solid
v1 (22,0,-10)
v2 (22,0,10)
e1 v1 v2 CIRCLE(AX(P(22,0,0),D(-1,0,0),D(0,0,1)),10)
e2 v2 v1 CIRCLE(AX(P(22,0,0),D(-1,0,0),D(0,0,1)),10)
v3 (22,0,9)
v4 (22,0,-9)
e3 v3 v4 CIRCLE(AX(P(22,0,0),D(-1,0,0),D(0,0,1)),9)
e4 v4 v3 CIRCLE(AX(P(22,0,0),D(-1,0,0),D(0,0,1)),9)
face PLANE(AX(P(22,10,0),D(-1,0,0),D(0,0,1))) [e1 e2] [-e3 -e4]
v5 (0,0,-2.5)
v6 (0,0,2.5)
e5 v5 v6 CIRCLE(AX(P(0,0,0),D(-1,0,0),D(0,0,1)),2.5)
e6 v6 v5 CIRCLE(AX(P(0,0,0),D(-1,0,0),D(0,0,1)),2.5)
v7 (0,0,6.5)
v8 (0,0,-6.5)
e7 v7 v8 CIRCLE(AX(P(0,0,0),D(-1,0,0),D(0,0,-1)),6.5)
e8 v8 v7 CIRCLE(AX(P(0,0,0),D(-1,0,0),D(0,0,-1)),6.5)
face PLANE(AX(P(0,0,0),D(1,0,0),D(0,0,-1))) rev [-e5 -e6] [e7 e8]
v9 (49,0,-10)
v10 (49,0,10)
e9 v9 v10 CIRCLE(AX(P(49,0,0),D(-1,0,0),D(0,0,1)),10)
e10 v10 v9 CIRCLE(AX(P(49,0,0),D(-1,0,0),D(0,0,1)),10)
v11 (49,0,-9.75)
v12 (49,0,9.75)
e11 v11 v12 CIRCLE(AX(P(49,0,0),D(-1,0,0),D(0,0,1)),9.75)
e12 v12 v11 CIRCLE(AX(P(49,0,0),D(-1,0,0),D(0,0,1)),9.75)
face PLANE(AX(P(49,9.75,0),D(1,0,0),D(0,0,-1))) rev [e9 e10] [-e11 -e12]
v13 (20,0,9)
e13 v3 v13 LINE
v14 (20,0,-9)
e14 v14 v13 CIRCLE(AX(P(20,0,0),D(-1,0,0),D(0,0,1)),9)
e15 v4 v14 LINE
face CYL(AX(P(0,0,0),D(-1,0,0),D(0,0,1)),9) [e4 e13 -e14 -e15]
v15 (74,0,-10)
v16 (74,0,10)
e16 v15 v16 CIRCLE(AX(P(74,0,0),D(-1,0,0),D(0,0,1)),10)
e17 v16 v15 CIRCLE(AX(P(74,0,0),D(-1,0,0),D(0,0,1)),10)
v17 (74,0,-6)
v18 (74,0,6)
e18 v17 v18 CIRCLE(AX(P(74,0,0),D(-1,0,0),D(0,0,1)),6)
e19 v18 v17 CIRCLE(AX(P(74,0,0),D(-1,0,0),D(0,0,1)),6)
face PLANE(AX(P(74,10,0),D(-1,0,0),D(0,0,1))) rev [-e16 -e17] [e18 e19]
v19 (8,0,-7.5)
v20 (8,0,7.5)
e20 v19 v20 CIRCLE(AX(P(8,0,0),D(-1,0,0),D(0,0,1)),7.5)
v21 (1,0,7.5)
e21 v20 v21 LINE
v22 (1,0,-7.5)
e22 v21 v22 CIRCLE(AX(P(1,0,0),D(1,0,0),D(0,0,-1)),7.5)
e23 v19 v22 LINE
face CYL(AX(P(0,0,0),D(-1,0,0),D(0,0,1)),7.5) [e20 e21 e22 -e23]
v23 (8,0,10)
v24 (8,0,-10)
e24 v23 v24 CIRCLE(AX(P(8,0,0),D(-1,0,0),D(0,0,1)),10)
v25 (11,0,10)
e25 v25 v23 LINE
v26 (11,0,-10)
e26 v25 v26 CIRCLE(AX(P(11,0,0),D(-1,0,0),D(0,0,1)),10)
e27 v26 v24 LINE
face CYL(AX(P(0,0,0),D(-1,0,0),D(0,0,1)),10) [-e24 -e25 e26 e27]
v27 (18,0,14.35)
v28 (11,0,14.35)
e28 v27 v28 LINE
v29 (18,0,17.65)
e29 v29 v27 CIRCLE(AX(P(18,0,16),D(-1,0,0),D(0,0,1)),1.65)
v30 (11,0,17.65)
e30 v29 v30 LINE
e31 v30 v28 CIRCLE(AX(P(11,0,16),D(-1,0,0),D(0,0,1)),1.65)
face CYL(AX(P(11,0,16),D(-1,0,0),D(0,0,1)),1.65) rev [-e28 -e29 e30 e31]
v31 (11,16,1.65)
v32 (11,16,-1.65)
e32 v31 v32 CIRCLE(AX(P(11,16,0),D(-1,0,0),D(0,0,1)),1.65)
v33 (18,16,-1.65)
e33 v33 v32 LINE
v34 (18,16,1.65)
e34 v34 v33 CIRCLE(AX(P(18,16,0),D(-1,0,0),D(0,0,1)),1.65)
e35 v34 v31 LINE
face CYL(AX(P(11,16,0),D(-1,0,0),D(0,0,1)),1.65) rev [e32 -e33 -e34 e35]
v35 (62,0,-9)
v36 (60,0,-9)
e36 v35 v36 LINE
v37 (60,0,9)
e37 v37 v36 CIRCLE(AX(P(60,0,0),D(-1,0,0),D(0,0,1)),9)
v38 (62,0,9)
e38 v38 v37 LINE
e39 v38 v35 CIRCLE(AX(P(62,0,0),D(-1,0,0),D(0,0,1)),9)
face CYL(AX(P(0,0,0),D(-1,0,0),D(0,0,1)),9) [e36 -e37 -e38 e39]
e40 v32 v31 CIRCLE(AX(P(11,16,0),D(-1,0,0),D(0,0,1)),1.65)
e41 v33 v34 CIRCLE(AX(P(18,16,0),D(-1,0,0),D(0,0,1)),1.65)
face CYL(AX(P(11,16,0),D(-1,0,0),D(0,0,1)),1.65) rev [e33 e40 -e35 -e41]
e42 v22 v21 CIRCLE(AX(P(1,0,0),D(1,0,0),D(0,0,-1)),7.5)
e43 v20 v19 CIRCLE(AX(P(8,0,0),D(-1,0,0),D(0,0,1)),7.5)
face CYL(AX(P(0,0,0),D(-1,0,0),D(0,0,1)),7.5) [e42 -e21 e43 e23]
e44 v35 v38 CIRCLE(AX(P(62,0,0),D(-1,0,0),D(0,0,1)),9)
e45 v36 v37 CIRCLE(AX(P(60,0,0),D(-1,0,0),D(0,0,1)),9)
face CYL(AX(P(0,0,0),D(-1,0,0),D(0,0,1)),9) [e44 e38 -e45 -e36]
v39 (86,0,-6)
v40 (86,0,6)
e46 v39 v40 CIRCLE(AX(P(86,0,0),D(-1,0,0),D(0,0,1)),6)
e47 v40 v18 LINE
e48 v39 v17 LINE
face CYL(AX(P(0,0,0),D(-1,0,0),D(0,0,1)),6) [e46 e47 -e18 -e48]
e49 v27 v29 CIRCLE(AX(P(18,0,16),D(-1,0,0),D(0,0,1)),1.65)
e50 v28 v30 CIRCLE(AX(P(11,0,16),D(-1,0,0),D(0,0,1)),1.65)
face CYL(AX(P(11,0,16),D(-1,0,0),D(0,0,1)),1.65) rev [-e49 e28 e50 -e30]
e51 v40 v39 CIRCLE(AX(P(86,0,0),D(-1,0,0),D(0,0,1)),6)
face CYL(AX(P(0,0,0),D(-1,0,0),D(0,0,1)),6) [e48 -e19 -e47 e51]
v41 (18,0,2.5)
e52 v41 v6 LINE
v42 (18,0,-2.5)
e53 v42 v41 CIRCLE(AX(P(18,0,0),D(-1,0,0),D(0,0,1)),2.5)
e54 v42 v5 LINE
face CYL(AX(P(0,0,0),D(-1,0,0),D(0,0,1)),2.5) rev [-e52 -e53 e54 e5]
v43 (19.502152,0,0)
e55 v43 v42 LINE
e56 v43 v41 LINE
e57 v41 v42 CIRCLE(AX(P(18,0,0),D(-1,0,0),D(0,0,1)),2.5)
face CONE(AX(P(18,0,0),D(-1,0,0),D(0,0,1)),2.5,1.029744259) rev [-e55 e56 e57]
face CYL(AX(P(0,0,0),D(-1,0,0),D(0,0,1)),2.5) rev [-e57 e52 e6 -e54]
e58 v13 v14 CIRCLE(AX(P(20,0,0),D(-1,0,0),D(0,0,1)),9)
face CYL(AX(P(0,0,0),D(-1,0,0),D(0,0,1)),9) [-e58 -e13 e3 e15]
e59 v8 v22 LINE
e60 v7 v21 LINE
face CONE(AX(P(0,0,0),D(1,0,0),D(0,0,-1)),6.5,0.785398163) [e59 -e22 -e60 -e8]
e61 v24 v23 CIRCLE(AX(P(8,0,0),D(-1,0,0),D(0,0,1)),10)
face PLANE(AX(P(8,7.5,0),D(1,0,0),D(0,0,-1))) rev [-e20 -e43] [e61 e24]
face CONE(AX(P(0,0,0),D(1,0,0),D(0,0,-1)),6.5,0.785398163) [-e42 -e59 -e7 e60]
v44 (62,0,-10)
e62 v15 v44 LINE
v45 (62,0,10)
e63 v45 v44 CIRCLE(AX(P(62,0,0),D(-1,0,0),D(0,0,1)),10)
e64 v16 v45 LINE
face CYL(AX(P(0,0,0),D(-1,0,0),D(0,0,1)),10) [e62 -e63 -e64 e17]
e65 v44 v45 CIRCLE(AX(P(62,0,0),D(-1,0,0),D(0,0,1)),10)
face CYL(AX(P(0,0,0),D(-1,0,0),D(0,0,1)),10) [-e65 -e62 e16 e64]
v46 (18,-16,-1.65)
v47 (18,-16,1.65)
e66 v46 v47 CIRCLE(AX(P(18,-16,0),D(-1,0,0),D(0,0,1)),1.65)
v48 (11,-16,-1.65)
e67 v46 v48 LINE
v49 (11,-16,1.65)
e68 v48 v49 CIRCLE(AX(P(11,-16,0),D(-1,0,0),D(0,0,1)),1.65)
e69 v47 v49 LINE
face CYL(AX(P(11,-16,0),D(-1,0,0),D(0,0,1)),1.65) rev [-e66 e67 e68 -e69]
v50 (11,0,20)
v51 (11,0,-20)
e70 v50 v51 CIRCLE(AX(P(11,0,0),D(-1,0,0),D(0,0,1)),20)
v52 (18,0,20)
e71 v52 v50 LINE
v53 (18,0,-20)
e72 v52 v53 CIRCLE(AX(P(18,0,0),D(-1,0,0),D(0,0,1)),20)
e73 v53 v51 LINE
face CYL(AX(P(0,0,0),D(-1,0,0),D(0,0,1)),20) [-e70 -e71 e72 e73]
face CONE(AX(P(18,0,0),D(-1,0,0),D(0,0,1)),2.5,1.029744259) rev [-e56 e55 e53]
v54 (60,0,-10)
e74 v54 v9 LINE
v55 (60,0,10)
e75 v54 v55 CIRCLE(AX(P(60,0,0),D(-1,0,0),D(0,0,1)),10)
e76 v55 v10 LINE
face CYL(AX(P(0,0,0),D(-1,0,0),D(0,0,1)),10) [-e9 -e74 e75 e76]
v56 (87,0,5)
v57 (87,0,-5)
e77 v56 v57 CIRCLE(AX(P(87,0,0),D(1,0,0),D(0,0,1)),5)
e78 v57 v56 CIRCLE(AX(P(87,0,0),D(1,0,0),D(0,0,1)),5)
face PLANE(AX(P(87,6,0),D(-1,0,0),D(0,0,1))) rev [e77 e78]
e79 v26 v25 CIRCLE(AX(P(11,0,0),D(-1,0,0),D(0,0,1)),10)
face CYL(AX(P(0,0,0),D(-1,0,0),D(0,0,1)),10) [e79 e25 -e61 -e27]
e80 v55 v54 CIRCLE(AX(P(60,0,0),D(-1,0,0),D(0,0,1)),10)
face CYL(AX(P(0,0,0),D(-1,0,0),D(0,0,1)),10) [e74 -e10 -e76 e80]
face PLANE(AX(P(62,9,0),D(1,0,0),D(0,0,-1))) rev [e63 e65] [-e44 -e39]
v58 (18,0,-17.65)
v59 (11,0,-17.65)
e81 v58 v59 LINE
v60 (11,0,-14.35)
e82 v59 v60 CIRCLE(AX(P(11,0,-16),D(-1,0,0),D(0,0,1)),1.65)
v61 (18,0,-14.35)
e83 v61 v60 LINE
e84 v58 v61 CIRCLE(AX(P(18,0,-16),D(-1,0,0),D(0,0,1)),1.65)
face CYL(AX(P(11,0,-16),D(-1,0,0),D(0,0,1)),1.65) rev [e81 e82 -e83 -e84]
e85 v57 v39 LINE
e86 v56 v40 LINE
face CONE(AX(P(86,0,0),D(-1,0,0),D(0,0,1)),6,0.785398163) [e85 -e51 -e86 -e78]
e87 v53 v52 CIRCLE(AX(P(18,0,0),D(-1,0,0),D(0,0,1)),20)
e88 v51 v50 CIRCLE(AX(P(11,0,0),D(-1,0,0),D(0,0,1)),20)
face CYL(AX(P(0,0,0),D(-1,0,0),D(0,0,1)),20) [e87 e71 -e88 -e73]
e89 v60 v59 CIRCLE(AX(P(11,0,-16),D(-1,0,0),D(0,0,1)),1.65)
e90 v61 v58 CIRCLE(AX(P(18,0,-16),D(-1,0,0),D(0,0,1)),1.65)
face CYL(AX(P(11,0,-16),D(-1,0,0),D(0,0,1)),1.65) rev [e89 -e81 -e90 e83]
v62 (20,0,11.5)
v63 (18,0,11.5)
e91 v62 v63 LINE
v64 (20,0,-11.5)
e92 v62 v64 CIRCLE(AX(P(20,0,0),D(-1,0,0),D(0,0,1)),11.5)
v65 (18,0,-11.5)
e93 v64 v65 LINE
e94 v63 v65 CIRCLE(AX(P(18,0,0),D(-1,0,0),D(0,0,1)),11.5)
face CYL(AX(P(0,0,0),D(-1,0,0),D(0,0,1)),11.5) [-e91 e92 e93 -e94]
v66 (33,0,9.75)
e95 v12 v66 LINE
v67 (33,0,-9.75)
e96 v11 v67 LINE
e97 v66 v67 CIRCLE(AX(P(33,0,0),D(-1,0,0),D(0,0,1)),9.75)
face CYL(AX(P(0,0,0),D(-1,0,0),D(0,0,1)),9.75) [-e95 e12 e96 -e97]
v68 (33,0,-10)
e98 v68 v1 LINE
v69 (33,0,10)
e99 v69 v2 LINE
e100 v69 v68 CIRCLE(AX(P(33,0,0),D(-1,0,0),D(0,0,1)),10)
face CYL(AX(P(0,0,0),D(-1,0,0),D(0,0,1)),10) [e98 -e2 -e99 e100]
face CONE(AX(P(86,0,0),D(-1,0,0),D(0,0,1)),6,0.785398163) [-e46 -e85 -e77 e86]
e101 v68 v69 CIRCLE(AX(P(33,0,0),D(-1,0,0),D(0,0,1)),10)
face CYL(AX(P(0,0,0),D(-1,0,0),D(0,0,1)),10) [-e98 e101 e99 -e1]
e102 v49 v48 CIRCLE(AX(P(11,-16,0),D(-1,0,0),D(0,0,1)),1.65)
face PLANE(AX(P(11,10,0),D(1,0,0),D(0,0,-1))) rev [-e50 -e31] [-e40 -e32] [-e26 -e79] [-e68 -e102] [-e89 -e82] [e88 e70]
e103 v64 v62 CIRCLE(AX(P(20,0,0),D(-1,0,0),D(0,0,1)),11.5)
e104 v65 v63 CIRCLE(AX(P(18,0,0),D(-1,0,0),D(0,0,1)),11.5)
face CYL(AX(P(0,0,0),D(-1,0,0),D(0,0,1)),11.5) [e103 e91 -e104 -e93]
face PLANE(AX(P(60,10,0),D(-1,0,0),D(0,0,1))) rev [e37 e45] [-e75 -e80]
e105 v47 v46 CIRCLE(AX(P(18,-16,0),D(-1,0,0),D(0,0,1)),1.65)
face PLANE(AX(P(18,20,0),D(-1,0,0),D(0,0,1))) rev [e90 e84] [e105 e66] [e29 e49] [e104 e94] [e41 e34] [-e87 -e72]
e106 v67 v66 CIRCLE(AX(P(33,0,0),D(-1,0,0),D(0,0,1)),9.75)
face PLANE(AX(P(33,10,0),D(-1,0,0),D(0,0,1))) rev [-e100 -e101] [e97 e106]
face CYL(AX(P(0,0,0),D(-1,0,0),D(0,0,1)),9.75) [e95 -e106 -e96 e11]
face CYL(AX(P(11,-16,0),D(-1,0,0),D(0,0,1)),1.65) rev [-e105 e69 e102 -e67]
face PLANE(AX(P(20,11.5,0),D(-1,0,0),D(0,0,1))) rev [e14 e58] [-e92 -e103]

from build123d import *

# Parameters (mm, degrees)
M6_TAPPED_HOLE1_D     = 5
M6_TAPPED_HOLE1_DEPTH = 18
M6_TAPPED_HOLE1_TIP   = 1.502151548
M4_TAPPED_HOLE1_D     = 3.3
SKETCH6_W             = 2
SKETCH6_H             = 1
CHAMFER1_SIZE         = 1


with BuildPart() as part:
    # Sketch1 → Revolve1 (revolve)
    with BuildSketch(Plane.XY, mode=Mode.PRIVATE) as revolve1_sk:
        Polygon((0, 0), (87, 0), (87, 6), (74, 6), (74, 10), (62, 10), (62, 9), (60, 9), (60, 10), (49, 10), (49, 9.75), (33, 9.75), (33, 10), (20, 10), (20, 11.5), (18, 11.5), (18, 20), (11, 20), (11, 10), (8, 10), (8, 7.5), (0, 7.5), align=None)
    revolve(revolve1_sk.sketch.rotate(Axis((0, 0, 0), (1, 0, 0)), 90), axis=Axis((0, 0, 0), (1, 0, 0)))

    # M6 Tapped Hole1
    with Locations(Plane.ZY):
        with Locations((0, 0)):
            Hole(M6_TAPPED_HOLE1_D / 2, depth=M6_TAPPED_HOLE1_DEPTH)
            with Locations((0, 0, -(M6_TAPPED_HOLE1_DEPTH + M6_TAPPED_HOLE1_TIP / 2))):  # 118° drill point
                Cone(0, M6_TAPPED_HOLE1_D / 2, M6_TAPPED_HOLE1_TIP, mode=Mode.SUBTRACT)

    # M4 Tapped Hole1 (through all)
    with Locations(Plane.ZY.offset(-11)):
        with Locations((0, 16), (-16, 0), (0, -16), (16, 0)):
            Hole(M4_TAPPED_HOLE1_D / 2)

    # Sketch6 → Cut-Revolve1 (revolve, cut)
    with BuildSketch(Plane.XY, mode=Mode.PRIVATE) as cut_revolve1_sk:
        with Locations((21, 9.5)):
            Rectangle(SKETCH6_W, SKETCH6_H)
    revolve(cut_revolve1_sk.sketch.rotate(Axis((0, 0, 0), (1, 0, 0)), 90), axis=Axis((0, 0, 0), (1, 0, 0)), mode=Mode.SUBTRACT)

    # Chamfer1
    chamfer1_edges = [part.edges().sort_by_distance(p)[0] for p in [
        (87, 0, -6),
        (0, 0, -7.5),
    ]]
    chamfer(chamfer1_edges, length=CHAMFER1_SIZE)


solid = part.part
